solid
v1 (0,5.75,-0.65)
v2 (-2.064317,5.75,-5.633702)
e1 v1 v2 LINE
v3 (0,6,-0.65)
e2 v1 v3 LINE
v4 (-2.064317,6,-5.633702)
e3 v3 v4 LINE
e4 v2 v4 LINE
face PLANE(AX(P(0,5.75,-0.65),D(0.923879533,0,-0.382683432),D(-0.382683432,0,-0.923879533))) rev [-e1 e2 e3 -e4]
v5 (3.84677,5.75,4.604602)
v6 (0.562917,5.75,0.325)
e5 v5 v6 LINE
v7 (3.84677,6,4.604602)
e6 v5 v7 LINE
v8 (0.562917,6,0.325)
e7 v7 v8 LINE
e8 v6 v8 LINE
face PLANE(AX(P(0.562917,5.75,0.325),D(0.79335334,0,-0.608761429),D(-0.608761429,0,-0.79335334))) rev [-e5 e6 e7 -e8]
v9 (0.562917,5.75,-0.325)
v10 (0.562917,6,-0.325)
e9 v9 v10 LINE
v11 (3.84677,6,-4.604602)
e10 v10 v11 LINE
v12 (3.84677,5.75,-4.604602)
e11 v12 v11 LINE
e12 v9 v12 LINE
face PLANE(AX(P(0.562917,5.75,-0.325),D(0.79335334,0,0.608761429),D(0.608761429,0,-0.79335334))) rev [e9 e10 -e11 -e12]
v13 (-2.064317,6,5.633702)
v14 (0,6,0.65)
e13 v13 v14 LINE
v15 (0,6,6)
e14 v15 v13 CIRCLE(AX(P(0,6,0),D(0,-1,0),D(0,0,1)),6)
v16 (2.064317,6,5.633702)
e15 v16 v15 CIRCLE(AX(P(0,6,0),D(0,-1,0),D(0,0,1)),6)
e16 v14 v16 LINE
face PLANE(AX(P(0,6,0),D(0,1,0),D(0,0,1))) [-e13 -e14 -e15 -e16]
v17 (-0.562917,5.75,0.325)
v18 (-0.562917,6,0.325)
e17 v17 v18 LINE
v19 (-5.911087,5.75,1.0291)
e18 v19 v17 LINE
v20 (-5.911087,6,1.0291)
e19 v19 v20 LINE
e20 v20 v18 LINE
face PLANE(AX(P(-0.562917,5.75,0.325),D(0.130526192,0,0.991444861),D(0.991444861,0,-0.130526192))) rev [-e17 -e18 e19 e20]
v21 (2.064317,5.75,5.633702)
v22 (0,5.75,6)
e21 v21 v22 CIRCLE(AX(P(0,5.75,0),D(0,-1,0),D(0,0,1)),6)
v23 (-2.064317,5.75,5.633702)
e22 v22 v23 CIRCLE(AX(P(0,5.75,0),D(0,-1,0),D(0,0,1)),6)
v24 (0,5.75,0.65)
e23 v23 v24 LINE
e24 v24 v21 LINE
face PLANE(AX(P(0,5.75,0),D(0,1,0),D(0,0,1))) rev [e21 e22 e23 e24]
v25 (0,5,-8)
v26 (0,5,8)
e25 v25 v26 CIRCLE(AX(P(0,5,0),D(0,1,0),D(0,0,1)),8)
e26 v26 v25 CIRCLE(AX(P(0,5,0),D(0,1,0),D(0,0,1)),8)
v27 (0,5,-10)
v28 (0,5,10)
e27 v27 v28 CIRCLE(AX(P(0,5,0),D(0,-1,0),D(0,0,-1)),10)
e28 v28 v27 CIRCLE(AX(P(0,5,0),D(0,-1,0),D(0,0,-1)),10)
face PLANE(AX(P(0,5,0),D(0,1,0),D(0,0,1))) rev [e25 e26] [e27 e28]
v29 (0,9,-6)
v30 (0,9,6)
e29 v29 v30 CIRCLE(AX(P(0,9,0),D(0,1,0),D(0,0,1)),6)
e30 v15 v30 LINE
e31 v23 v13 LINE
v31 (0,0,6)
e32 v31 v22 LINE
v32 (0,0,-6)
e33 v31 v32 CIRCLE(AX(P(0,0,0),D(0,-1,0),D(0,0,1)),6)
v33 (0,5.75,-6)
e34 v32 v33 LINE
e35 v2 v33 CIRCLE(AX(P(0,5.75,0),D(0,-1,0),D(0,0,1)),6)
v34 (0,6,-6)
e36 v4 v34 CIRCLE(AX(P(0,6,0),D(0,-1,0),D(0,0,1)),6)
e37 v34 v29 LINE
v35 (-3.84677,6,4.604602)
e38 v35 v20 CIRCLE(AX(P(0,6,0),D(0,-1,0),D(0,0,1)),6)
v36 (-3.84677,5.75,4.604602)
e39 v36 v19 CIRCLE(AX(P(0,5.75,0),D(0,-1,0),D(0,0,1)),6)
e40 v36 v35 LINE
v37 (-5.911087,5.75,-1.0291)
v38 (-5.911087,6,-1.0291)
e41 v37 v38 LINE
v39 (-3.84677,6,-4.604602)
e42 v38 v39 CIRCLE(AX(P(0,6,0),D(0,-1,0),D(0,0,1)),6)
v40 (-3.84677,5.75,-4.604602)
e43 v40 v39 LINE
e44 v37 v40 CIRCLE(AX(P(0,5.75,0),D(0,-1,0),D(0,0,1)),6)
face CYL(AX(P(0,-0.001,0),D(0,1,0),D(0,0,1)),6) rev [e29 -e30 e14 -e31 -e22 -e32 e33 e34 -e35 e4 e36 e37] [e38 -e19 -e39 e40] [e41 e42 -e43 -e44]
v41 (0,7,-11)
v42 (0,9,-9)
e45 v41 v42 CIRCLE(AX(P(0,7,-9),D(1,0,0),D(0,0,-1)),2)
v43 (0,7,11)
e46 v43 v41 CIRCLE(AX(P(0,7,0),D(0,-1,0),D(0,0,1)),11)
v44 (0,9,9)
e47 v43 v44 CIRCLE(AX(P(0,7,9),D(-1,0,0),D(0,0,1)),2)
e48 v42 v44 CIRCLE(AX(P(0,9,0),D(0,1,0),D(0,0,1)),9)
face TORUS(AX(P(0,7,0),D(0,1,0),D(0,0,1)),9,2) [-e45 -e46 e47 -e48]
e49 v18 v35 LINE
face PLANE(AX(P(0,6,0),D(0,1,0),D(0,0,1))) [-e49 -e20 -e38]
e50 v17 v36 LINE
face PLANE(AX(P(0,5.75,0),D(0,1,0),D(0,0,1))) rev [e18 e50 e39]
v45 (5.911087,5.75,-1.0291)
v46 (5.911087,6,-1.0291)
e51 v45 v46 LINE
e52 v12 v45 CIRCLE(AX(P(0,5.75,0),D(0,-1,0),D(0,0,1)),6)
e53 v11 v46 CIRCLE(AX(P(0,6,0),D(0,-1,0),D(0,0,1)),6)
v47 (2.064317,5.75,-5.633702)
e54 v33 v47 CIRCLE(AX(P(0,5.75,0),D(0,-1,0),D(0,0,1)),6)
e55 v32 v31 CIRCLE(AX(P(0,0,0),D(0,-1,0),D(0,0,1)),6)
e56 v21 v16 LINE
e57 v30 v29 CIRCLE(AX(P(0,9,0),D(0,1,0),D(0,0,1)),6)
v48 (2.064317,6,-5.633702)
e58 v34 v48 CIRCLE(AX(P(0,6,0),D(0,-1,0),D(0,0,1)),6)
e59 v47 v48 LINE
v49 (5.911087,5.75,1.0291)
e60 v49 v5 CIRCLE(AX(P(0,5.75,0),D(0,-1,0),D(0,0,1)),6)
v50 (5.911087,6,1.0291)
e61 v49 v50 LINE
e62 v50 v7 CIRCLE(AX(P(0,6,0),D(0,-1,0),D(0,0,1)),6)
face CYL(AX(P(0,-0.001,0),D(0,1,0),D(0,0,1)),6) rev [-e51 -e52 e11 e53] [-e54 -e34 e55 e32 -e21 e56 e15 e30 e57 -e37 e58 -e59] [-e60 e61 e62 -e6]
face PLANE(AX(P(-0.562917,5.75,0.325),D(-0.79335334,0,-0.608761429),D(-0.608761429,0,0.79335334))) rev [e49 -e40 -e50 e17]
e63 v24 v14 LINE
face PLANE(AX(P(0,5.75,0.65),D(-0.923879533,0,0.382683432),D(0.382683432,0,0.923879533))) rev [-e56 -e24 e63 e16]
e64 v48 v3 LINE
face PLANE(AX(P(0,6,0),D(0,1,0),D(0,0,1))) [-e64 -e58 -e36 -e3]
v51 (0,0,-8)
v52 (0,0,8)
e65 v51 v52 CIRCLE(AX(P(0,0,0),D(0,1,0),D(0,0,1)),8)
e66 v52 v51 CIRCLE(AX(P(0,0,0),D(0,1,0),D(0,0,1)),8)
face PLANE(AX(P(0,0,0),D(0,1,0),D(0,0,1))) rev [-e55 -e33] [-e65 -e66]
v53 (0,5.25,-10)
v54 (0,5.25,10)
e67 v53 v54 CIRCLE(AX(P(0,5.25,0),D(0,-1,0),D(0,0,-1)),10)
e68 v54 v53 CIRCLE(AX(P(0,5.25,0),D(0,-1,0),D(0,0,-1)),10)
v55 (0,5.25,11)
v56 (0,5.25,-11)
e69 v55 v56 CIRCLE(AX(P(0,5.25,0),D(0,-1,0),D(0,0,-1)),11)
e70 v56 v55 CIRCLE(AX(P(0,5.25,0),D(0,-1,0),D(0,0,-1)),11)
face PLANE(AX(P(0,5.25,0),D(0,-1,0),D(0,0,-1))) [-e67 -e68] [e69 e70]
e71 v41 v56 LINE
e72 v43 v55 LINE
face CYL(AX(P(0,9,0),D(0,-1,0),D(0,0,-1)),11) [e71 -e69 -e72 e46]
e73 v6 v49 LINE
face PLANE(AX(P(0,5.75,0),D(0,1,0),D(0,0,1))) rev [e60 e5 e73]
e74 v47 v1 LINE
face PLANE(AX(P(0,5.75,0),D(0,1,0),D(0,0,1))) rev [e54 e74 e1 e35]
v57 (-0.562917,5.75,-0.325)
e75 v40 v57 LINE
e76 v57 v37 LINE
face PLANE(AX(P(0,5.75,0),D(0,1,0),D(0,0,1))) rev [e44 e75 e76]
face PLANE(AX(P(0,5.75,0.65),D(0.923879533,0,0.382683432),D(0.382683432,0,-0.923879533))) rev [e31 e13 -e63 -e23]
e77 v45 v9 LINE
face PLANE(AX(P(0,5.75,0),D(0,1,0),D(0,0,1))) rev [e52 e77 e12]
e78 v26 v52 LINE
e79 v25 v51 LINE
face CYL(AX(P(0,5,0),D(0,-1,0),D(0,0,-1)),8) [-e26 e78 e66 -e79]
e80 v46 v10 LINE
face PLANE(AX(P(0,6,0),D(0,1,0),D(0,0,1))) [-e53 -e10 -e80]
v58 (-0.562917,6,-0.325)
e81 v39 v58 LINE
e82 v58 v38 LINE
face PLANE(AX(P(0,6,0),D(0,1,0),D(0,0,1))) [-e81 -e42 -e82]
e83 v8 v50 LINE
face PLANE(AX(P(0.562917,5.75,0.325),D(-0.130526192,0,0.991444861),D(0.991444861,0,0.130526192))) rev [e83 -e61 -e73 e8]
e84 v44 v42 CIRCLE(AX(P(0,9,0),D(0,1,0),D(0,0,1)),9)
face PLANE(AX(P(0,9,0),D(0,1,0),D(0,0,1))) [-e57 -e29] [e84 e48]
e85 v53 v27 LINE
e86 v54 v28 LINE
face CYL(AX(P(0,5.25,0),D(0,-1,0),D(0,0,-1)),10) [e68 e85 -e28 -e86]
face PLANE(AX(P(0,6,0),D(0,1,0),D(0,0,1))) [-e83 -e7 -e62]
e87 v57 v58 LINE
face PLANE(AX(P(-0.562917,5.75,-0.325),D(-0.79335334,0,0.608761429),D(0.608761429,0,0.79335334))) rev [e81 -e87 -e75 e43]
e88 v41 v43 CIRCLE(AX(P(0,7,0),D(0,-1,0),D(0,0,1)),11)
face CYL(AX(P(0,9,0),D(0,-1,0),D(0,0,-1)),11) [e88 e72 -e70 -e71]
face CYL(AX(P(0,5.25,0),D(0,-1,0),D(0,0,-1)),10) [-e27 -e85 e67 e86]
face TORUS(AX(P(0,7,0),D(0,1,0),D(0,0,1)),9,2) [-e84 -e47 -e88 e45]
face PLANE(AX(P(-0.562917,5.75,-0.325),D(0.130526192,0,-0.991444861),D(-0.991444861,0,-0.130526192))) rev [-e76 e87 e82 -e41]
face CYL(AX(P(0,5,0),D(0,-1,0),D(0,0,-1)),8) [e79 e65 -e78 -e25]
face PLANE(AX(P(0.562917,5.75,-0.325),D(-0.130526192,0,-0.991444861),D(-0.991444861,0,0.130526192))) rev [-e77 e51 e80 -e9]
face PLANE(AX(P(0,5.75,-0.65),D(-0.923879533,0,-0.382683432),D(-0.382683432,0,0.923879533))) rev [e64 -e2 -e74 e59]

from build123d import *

# Parameters (mm, degrees)
SKETCH1_R           = 8
BOSS_EXTRUDE1_DEPTH = 5
SKETCH2_R           = 11
BOSS_EXTRUDE2_DEPTH = 4
CUT_EXTRUDE1_REACH  = 19.972
SKETCH3_R           = 6
BOSS_EXTRUDE3_START = -6
BOSS_EXTRUDE3_DEPTH = 0.25
SKETCH5_R           = 11
SKETCH5_R_2         = 10
CUT_EXTRUDE2_DEPTH  = 0.25
FILLET1_R           = 2


with BuildPart() as part:
    # Sketch1 → Boss-Extrude1 (new body)
    with BuildSketch(Plane(origin=(0, 0, 0), x_dir=(1, 0, 0), z_dir=(0, 1, 0))):
        with Locations(Location((0, 0, 0), (0, 0, 270))):
            Circle(SKETCH1_R)
    extrude(amount=BOSS_EXTRUDE1_DEPTH)

    # Sketch2 → Boss-Extrude2 (add)
    with BuildSketch(Plane(origin=(0, 5, 0), x_dir=(1, 0, 0), z_dir=(0, 1, 0))):
        with Locations(Location((0, 0, 0), (0, 0, 270))):
            Circle(SKETCH2_R)
    extrude(amount=BOSS_EXTRUDE2_DEPTH)

    # Sketch3 → Cut-Extrude1 (cut, up to next)
    with BuildSketch(Plane(origin=(0, 9, 0), x_dir=(1, 0, 0), z_dir=(0, 1, 0)), mode=Mode.PRIVATE) as cut_extrude1_sk1:
        with Locations(Location((0, 0, 0), (0, 0, 270))):
            Circle(SKETCH3_R)
    cut_extrude1_tool1 = extrude(cut_extrude1_sk1.sketch, amount=-CUT_EXTRUDE1_REACH, mode=Mode.PRIVATE) & part.part
    add(cut_extrude1_tool1.solids().sort_by_distance((0, 9, 0))[0], mode=Mode.SUBTRACT)

    # Sketch4 → Boss-Extrude3 (add)
    with BuildSketch(Plane.XZ.offset(BOSS_EXTRUDE3_START)):
        with BuildLine():
            Line((0, 0.65), (-2.064316872, 5.633701789))
            ThreePointArc((-2.064316872, 5.633701789), (0, 6), (2.064316872, 5.633701789))
            Line((2.064316872, 5.633701789), (0, 0.65))
        make_face()
        with BuildLine():
            Line((0.562916512, 0.325), (3.846770431, 4.604601747))
            ThreePointArc((3.846770431, 4.604601747), (5.196152423, 3), (5.911087303, 1.029100042))
            Line((5.911087303, 1.029100042), (0.562916512, 0.325))
        make_face()
        with BuildLine():
            Line((0.562916512, -0.325), (5.911087303, -1.029100042))
            ThreePointArc((5.911087303, -1.029100042), (5.196152423, -3), (3.846770431, -4.604601747))
            Line((3.846770431, -4.604601747), (0.562916512, -0.325))
        make_face()
        with BuildLine():
            Line((0, -0.65), (2.064316872, -5.633701789))
            ThreePointArc((2.064316872, -5.633701789), (0, -6), (-2.064316872, -5.633701789))
            Line((-2.064316872, -5.633701789), (0, -0.65))
        make_face()
        with BuildLine():
            Line((-0.562916512, -0.325), (-3.846770431, -4.604601747))
            ThreePointArc((-3.846770431, -4.604601747), (-5.196152423, -3), (-5.911087303, -1.029100042))
            Line((-5.911087303, -1.029100042), (-0.562916512, -0.325))
        make_face()
        with BuildLine():
            Line((-0.562916512, 0.325), (-5.911087303, 1.029100042))
            ThreePointArc((-5.911087303, 1.029100042), (-5.196152423, 3), (-3.846770431, 4.604601747))
            Line((-3.846770431, 4.604601747), (-0.562916512, 0.325))
        make_face()
    extrude(amount=BOSS_EXTRUDE3_DEPTH)

    # Sketch5 → Cut-Extrude2 (cut)
    with BuildSketch(Plane.XZ.offset(-5)):
        with Locations(Location((0, 0, 0), (0, 0, 270))):
            Circle(SKETCH5_R)
        with Locations(Location((0, 0, 0), (0, 0, 270))):
            Circle(SKETCH5_R_2, mode=Mode.SUBTRACT)
    extrude(amount=-CUT_EXTRUDE2_DEPTH, mode=Mode.SUBTRACT)

    # Fillet1
    fillet1_edges = [part.edges().sort_by_distance(p)[0] for p in [
        (0, 9, -11),
    ]]
    fillet(fillet1_edges, radius=FILLET1_R)


solid = part.part
